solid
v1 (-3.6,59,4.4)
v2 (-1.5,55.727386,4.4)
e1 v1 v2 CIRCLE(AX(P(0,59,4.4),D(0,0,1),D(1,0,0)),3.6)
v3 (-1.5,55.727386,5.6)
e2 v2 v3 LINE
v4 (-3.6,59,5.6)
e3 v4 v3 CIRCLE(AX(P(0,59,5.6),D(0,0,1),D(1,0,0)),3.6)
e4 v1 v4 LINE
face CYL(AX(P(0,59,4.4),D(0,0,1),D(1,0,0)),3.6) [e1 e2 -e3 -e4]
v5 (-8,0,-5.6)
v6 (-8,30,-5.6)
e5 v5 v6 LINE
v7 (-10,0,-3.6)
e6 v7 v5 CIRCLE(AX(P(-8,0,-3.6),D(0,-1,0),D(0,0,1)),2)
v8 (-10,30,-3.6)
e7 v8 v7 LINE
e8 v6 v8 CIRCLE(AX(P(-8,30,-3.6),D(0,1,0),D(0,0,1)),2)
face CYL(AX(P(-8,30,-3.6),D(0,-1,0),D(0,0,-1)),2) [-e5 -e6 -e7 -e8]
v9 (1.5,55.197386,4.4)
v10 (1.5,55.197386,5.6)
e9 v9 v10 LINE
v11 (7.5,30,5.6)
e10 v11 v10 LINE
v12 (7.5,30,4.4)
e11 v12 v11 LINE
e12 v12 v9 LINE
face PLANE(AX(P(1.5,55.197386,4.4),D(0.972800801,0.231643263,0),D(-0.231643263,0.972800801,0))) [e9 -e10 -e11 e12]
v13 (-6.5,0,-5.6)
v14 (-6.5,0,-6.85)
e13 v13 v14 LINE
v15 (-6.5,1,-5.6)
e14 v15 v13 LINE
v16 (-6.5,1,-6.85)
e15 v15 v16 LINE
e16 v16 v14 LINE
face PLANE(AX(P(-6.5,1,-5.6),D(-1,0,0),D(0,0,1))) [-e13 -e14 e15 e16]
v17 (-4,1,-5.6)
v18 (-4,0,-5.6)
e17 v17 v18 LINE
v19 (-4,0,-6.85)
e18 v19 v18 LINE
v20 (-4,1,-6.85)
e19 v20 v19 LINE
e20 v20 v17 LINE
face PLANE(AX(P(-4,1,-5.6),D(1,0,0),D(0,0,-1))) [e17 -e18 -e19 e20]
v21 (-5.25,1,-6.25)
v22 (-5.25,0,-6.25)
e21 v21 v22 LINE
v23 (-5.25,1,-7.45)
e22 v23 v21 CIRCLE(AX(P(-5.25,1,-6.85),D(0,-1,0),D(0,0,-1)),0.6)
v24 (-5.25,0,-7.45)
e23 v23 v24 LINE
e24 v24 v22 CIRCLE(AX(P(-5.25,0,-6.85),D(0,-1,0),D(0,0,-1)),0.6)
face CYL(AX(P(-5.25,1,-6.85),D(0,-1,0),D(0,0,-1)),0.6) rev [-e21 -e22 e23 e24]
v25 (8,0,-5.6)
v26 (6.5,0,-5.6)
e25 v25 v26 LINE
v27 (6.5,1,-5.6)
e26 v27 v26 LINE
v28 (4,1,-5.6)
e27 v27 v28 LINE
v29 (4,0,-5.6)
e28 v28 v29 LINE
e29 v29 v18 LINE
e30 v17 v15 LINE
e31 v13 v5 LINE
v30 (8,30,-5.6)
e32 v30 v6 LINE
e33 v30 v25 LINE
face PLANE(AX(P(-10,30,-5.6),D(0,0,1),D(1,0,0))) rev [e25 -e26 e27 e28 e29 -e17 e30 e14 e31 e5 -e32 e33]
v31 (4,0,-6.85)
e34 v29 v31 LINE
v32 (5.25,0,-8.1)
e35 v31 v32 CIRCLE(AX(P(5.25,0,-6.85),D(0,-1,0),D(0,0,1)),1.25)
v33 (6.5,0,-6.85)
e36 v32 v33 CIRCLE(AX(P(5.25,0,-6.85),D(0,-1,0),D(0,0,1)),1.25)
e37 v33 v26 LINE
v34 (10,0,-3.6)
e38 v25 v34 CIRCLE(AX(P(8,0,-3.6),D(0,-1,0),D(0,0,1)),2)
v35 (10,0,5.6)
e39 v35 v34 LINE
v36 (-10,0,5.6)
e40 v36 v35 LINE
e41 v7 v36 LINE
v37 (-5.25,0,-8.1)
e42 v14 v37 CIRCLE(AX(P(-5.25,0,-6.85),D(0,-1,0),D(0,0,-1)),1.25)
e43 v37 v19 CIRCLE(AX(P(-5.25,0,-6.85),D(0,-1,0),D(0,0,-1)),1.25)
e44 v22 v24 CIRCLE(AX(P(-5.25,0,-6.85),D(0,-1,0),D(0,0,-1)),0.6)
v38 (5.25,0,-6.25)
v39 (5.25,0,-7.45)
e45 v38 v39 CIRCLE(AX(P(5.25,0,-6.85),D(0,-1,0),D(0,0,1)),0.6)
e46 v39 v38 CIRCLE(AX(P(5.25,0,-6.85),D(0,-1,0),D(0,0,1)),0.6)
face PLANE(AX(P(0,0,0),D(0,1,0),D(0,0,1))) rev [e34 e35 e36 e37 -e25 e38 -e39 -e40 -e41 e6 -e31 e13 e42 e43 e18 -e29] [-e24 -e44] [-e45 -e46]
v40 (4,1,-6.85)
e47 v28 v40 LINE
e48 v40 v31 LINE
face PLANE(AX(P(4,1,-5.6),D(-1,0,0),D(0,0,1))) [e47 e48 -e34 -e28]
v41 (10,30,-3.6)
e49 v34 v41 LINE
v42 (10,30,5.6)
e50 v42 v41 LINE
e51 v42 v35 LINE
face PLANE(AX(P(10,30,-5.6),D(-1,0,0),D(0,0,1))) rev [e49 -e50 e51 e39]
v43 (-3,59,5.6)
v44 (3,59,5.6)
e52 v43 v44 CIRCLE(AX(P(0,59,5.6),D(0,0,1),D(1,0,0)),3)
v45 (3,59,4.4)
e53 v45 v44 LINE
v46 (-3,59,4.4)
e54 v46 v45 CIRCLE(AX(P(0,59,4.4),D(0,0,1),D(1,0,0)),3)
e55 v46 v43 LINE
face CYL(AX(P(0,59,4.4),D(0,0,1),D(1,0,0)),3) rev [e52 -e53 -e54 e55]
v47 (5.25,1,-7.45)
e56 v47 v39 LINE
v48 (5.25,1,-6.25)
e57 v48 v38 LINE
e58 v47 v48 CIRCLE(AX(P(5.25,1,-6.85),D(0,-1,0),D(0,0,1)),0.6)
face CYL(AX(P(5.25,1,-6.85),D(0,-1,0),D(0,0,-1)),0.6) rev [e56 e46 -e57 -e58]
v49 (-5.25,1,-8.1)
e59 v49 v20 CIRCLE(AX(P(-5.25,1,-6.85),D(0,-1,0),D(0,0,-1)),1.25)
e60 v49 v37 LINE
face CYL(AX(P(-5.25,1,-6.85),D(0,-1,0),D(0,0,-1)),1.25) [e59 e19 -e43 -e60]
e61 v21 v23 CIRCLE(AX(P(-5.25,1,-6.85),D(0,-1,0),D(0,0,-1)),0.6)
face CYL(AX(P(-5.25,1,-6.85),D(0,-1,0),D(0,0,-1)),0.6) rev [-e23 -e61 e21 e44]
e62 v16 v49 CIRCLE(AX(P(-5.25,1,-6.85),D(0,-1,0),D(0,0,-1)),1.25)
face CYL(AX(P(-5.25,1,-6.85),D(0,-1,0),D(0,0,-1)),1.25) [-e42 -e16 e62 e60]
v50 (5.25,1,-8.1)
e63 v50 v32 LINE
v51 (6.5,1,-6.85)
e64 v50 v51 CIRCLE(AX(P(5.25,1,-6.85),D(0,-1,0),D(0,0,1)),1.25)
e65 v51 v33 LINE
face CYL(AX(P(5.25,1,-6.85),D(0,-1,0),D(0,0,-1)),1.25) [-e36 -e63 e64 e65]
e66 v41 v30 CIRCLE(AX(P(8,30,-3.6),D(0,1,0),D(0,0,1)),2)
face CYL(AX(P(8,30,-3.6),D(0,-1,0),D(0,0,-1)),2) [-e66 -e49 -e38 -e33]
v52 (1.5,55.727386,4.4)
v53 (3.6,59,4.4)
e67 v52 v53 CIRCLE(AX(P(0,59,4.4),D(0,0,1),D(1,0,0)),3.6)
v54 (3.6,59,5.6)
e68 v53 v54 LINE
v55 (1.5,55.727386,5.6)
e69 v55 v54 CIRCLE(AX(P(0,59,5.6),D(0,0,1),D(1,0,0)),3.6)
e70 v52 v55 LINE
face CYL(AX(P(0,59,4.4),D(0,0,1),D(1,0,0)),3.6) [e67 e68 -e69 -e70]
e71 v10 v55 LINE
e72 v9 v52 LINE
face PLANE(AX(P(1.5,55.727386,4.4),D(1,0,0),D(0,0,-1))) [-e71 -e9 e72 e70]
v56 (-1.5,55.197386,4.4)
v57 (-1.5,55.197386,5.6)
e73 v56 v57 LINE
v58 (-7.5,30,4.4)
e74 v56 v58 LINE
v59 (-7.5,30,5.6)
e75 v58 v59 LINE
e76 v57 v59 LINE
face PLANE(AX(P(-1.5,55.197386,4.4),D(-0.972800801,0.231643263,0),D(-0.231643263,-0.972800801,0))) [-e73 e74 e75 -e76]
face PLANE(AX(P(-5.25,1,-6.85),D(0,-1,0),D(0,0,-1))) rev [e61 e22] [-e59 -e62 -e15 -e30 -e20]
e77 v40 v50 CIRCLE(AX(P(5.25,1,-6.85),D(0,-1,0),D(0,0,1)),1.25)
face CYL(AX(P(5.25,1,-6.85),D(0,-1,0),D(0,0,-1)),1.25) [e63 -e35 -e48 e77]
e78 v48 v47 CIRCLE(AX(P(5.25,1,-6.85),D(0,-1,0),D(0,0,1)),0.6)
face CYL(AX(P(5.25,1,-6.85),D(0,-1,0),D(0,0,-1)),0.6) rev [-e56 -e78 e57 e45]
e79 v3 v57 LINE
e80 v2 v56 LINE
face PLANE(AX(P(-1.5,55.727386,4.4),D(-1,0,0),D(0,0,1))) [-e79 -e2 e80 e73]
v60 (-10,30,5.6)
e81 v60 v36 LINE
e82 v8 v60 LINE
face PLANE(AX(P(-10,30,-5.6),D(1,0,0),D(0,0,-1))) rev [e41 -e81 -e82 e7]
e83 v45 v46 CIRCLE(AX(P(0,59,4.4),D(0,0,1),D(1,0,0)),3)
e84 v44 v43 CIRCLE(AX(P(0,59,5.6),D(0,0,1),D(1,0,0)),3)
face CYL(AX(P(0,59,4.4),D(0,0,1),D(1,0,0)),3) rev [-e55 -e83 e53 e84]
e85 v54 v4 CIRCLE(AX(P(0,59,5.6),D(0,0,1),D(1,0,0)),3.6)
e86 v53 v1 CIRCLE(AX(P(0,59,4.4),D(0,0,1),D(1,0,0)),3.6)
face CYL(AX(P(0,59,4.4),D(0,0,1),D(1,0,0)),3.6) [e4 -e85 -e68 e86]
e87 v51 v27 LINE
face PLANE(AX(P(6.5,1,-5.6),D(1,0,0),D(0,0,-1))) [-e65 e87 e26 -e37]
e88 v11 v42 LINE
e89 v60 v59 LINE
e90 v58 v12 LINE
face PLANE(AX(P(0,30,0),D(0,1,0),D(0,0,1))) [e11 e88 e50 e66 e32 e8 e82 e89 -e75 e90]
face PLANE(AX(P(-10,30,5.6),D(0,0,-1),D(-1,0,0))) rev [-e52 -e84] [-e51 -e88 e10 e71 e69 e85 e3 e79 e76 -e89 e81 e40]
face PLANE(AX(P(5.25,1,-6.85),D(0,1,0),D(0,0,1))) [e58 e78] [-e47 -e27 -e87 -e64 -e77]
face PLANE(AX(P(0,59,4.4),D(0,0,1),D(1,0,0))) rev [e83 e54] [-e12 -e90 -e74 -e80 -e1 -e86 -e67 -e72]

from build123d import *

# Parameters (mm, degrees)
SKETCH1_W           = 20
SKETCH1_H           = 11.2
BOSS_EXTRUDE1_DEPTH = 30
SKETCH2_R           = 3
BOSS_EXTRUDE2_DEPTH = 1.2
FILLET1_R           = 2
SKETCH3_R           = 0.6
BOSS_EXTRUDE3_DEPTH = 1


with BuildPart() as part:
    # Sketch1 → Boss-Extrude1 (new body)
    with BuildSketch(Plane(origin=(0, 0, 0), x_dir=(1, 0, 0), z_dir=(0, 1, 0))):
        Rectangle(SKETCH1_W, SKETCH1_H)
    extrude(amount=BOSS_EXTRUDE1_DEPTH)

    # Sketch2 → Boss-Extrude2 (add)
    with BuildSketch(Plane.XY.offset(5.6)):
        with BuildLine():
            Line((-1.5, 55.197386366), (-7.5, 30))
            Line((-7.5, 30), (7.5, 30))
            Line((7.5, 30), (1.5, 55.197386366))
            Line((1.5, 55.197386366), (1.5, 55.727386366))
            ThreePointArc((1.5, 55.727386366), (0, 62.6), (-1.5, 55.727386366))
            Line((-1.5, 55.727386366), (-1.5, 55.197386366))
        make_face()
        with Locations((0, 59)):
            Circle(SKETCH2_R, mode=Mode.SUBTRACT)
    extrude(amount=-BOSS_EXTRUDE2_DEPTH)

    # Fillet1
    fillet1_edges = [part.edges().sort_by_distance(p)[0] for p in [
        (-10, 15, -5.6),
        (10, 15, -5.6),
    ]]
    fillet(fillet1_edges, radius=FILLET1_R)

    # Sketch3 → Boss-Extrude3 (add)
    # profile 1 of 2: a face of its own
    with BuildSketch(Plane.XZ):
        with BuildLine():
            Line((6.5, -5.6), (4, -5.6))
            Line((4, -5.6), (4, -6.85))
            ThreePointArc((4, -6.85), (5.25, -8.1), (6.5, -6.85))
            Line((6.5, -6.85), (6.5, -5.6))
        make_face()
        with Locations(Location((5.25, -6.85, 0), (0, 0, 90))):
            Circle(SKETCH3_R, mode=Mode.SUBTRACT)
    # profile 2 of 2: a face of its own
    with BuildSketch(Plane.XZ):
        with BuildLine():
            Line((-6.5, -5.6), (-4, -5.6))
            Line((-4, -5.6), (-4, -6.85))
            ThreePointArc((-4, -6.85), (-5.25, -8.1), (-6.5, -6.85))
            Line((-6.5, -6.85), (-6.5, -5.6))
        make_face()
        with Locations(Location((-5.25, -6.85, 0), (0, 0, 270))):
            Circle(SKETCH3_R, mode=Mode.SUBTRACT)
    extrude(amount=-BOSS_EXTRUDE3_DEPTH)


solid = part.part
